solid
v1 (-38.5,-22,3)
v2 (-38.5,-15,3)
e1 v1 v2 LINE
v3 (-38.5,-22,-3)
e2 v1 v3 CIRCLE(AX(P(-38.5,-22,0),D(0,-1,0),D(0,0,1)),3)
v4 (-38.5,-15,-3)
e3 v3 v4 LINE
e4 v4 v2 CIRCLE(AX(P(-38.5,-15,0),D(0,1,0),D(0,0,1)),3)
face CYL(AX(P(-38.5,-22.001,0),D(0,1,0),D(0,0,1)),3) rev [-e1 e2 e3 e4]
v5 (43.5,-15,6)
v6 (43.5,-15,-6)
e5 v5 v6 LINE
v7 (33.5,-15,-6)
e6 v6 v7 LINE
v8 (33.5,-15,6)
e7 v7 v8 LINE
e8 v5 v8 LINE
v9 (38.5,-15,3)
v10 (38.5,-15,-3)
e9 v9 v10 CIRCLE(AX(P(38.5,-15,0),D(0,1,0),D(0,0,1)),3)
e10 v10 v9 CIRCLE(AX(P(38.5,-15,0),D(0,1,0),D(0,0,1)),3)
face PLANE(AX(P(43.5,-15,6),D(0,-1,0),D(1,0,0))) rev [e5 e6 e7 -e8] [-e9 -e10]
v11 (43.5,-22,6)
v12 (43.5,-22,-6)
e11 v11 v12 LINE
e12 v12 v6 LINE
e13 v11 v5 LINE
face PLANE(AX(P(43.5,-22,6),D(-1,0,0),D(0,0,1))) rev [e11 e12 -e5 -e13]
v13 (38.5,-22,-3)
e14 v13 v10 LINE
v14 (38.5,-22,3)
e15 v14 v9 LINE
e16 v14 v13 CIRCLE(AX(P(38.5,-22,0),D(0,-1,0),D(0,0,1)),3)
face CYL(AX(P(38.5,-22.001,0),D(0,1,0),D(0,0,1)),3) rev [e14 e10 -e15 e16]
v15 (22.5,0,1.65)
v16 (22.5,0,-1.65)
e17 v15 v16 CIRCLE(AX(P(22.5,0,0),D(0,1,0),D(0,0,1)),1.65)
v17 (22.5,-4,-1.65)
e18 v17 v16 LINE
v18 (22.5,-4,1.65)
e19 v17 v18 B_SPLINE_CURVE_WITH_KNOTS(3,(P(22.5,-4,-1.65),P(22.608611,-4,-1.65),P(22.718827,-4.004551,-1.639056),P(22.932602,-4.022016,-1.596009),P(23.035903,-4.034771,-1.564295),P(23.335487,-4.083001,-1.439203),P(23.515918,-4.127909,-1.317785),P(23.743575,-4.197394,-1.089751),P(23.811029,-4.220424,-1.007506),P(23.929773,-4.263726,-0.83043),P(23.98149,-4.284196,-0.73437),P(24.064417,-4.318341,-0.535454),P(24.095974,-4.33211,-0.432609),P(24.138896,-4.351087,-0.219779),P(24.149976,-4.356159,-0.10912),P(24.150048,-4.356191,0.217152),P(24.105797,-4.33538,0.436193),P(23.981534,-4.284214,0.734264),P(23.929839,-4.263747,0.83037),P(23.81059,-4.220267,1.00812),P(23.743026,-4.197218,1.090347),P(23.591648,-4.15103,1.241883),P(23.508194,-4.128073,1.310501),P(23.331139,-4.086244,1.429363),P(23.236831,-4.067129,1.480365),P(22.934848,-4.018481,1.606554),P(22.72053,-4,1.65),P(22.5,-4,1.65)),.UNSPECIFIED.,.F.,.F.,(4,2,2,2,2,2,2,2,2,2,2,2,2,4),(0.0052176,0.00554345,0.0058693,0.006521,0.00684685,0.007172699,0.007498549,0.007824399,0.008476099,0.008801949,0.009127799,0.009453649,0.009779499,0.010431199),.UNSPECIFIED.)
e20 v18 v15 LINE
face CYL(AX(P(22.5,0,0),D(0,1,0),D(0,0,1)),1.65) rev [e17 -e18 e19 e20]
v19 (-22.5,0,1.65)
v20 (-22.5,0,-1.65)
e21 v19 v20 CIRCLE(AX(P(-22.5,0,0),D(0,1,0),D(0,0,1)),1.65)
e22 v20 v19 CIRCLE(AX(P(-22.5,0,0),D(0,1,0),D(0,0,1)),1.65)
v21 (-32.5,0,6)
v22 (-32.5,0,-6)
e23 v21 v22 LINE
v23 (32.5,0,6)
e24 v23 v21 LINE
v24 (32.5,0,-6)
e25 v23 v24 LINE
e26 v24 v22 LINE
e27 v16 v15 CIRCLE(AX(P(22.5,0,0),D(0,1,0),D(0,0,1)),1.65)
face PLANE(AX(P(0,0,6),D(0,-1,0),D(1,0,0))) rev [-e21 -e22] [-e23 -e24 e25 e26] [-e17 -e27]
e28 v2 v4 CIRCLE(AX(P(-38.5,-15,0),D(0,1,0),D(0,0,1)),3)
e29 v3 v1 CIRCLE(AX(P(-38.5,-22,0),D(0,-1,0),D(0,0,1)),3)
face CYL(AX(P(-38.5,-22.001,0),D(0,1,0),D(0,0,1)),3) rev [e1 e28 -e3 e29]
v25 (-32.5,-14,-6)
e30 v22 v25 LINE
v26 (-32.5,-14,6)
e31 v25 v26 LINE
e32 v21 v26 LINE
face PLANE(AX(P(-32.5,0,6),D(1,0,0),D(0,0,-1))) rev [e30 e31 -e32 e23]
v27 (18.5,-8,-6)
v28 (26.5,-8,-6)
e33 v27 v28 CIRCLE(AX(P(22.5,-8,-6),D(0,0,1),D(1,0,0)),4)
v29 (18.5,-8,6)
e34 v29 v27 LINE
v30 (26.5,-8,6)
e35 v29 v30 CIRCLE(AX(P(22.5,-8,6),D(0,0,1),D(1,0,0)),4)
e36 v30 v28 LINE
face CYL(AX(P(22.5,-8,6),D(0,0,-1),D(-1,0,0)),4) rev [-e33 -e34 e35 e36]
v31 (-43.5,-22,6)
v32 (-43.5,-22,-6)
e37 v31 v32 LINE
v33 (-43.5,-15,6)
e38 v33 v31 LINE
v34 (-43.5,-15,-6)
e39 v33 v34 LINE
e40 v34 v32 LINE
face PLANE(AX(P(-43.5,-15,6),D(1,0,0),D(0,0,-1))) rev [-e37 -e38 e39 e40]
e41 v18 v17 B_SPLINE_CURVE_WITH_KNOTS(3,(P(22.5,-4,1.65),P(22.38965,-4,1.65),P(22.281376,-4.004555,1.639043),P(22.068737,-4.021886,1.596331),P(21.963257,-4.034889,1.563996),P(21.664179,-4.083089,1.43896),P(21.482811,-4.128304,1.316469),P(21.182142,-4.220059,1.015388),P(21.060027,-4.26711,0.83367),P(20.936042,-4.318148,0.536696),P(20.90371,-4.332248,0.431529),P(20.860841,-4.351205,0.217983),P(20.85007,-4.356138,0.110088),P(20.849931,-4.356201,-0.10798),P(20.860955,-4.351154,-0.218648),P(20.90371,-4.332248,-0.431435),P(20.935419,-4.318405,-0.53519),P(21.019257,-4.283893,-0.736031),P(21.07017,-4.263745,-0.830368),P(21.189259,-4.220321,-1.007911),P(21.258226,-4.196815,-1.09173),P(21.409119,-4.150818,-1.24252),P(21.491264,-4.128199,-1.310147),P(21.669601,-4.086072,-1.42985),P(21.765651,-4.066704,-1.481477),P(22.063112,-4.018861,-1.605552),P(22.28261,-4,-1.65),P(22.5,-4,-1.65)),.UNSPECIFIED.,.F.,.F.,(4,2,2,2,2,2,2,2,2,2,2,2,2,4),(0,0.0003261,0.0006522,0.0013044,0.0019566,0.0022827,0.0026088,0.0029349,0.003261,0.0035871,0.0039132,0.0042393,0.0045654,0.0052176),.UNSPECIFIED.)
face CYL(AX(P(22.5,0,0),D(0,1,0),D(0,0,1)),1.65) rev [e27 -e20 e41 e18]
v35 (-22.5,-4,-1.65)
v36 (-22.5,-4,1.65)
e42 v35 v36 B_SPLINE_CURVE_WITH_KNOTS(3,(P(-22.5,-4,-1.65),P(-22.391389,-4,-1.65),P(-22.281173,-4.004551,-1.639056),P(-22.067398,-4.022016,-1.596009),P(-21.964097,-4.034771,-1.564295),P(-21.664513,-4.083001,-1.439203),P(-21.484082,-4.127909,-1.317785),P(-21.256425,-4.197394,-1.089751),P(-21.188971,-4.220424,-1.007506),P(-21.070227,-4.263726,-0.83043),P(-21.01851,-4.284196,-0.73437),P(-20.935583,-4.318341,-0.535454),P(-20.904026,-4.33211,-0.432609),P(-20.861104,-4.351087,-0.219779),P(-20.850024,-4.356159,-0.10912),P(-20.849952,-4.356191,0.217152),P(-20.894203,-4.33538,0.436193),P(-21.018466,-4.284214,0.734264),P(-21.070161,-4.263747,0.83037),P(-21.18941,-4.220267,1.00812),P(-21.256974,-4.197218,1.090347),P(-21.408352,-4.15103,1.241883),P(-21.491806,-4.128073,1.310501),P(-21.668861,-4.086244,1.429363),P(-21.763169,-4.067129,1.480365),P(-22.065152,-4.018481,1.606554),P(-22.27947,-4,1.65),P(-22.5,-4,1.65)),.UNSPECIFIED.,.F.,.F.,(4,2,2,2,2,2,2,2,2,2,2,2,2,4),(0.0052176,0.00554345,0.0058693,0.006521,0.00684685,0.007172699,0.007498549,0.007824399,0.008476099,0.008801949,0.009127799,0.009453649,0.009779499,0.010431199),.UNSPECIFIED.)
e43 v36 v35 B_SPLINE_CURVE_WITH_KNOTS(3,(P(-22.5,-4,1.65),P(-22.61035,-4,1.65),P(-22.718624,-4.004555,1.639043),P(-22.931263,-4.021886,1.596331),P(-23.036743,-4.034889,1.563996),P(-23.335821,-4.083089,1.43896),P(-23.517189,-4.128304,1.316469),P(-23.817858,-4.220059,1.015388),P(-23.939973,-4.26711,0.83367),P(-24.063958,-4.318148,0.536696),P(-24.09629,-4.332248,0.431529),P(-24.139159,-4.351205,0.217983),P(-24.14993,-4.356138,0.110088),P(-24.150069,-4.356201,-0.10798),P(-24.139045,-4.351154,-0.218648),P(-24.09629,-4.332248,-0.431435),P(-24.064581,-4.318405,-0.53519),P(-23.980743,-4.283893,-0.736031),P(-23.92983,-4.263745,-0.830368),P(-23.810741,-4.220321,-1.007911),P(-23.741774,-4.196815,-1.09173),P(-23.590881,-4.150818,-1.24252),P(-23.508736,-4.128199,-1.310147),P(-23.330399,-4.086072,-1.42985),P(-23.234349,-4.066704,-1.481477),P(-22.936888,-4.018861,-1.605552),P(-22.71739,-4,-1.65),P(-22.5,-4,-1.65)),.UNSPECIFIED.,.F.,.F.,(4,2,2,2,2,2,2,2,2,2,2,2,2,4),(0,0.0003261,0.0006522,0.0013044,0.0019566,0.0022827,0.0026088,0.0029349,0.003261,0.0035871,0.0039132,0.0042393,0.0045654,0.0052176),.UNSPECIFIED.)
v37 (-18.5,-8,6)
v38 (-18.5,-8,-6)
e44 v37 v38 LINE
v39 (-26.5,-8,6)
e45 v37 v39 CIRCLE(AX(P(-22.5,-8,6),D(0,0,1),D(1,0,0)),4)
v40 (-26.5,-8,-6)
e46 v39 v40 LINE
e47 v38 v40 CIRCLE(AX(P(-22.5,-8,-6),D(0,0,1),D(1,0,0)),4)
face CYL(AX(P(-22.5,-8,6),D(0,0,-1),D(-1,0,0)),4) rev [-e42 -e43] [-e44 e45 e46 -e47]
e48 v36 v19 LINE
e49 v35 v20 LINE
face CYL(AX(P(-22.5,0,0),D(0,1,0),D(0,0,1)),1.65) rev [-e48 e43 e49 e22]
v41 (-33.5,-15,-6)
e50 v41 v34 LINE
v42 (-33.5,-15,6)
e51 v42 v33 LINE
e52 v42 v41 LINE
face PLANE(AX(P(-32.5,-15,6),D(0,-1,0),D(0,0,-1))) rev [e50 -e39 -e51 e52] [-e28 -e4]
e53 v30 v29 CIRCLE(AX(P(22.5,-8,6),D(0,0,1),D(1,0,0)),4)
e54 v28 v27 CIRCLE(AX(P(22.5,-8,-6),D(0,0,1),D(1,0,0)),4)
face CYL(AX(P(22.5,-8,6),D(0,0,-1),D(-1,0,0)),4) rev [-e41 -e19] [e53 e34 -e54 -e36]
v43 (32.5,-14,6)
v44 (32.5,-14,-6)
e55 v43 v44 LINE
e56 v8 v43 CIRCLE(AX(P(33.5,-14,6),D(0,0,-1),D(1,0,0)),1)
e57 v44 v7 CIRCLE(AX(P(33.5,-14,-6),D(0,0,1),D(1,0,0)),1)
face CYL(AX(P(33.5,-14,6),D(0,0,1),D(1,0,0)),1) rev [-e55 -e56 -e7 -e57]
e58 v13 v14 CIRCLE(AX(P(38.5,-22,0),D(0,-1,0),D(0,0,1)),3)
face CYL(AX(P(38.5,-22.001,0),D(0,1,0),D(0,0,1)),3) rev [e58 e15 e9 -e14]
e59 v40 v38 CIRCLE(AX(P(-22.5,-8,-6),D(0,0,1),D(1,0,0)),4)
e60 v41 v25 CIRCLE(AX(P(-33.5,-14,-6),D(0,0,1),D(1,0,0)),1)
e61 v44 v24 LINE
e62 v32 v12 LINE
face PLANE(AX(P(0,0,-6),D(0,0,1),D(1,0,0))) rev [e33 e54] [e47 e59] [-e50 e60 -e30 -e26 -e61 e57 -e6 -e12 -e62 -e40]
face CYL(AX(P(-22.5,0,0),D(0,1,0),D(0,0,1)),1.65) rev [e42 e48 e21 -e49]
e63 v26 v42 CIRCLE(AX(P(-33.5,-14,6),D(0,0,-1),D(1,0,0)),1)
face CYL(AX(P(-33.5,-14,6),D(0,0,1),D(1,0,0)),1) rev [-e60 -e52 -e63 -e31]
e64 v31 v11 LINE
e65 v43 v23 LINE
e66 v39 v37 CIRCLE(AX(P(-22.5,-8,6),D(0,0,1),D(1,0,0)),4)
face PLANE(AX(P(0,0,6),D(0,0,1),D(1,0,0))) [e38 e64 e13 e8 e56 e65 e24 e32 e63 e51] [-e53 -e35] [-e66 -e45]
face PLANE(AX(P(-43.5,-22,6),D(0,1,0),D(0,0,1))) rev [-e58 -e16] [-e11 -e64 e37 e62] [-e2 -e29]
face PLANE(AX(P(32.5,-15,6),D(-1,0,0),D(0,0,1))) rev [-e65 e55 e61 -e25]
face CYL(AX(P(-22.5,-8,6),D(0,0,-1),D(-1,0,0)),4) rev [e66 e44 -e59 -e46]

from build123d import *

# Parameters (mm, degrees)
SKETCH_1_R              = 4
EXTRUDE_1_DEPTH         = 6
HOLE_WIZARD_M4_1_REACH  = 71.828
HOLE_WIZARD_M4_1_BORE_R = 1.65
FILLET_1_R              = 1
CUT_EXTRUDE_1_REACH     = 48.403
SKETCH_3_R              = 3


with BuildPart() as part:
    # 草图1 → 凸台-拉伸1 (new, symmetric)
    with BuildSketch(Plane.XY):
        Polygon((0, 0), (-32.5, 0), (-32.5, -15), (-43.5, -15), (-43.5, -22), (43.5, -22), (43.5, -15), (32.5, -15), (32.5, 0), align=None)
        with Locations((-22.5, -8)):
            Circle(SKETCH_1_R, mode=Mode.SUBTRACT)
        with Locations((22.5, -8)):
            Circle(SKETCH_1_R, mode=Mode.SUBTRACT)
    extrude(amount=EXTRUDE_1_DEPTH, both=True)

    # M4 螺纹孔1 bore (on position points) → M4 螺纹孔1 (cut, up to next)
    with BuildSketch(Plane(origin=(-22.5, 0, 0), x_dir=(1, 0, 0), z_dir=(0, 1, 0)), mode=Mode.PRIVATE) as hole_wizard_m4_1_sk1:
        Circle(HOLE_WIZARD_M4_1_BORE_R)
    hole_wizard_m4_1_tool1 = extrude(hole_wizard_m4_1_sk1.sketch, amount=-HOLE_WIZARD_M4_1_REACH, mode=Mode.PRIVATE) & part.part
    hole_wizard_m4_1 = hole_wizard_m4_1_tool1.solids().sort_by_distance((-22.5, 0, 0))[0]
    add(hole_wizard_m4_1, mode=Mode.SUBTRACT)

    # 镜向1: M4 螺纹孔1 across plane
    add(hole_wizard_m4_1.mirror(Plane(origin=(0, 0, 0), x_dir=(0, 0, 1), z_dir=(1, 0, 0))), mode=Mode.SUBTRACT)

    # 圆角1
    fillet_1_edges = [part.edges().sort_by_distance(p)[0] for p in [
        (32.5, -15, 0),
        (-32.5, -15, 0),
    ]]
    fillet(fillet_1_edges, radius=FILLET_1_R)

    # 草图3 → 切除-拉伸1 (cut, up to next)
    with BuildSketch(Plane(origin=(0, -15, 0), x_dir=(1, 0, 0), z_dir=(0, 1, 0)), mode=Mode.PRIVATE) as cut_extrude_1_sk1:
        with Locations(Location((-38.5, 0, 0), (0, 0, 270))):
            Circle(SKETCH_3_R)
    cut_extrude_1_tool1 = extrude(cut_extrude_1_sk1.sketch, amount=-CUT_EXTRUDE_1_REACH, mode=Mode.PRIVATE) & part.part
    # 草图3 → 切除-拉伸1 (cut, up to next)
    with BuildSketch(Plane(origin=(0, -15, 0), x_dir=(1, 0, 0), z_dir=(0, 1, 0)), mode=Mode.PRIVATE) as cut_extrude_1_sk2:
        with Locations(Location((38.5, 0, 0), (0, 0, 270))):
            Circle(SKETCH_3_R)
    cut_extrude_1_tool2 = extrude(cut_extrude_1_sk2.sketch, amount=-CUT_EXTRUDE_1_REACH, mode=Mode.PRIVATE) & part.part
    add(cut_extrude_1_tool1.solids().sort_by_distance((-38.5, -15, 0))[0], mode=Mode.SUBTRACT)
    add(cut_extrude_1_tool2.solids().sort_by_distance((38.5, -15, 0))[0], mode=Mode.SUBTRACT)


solid = part.part
